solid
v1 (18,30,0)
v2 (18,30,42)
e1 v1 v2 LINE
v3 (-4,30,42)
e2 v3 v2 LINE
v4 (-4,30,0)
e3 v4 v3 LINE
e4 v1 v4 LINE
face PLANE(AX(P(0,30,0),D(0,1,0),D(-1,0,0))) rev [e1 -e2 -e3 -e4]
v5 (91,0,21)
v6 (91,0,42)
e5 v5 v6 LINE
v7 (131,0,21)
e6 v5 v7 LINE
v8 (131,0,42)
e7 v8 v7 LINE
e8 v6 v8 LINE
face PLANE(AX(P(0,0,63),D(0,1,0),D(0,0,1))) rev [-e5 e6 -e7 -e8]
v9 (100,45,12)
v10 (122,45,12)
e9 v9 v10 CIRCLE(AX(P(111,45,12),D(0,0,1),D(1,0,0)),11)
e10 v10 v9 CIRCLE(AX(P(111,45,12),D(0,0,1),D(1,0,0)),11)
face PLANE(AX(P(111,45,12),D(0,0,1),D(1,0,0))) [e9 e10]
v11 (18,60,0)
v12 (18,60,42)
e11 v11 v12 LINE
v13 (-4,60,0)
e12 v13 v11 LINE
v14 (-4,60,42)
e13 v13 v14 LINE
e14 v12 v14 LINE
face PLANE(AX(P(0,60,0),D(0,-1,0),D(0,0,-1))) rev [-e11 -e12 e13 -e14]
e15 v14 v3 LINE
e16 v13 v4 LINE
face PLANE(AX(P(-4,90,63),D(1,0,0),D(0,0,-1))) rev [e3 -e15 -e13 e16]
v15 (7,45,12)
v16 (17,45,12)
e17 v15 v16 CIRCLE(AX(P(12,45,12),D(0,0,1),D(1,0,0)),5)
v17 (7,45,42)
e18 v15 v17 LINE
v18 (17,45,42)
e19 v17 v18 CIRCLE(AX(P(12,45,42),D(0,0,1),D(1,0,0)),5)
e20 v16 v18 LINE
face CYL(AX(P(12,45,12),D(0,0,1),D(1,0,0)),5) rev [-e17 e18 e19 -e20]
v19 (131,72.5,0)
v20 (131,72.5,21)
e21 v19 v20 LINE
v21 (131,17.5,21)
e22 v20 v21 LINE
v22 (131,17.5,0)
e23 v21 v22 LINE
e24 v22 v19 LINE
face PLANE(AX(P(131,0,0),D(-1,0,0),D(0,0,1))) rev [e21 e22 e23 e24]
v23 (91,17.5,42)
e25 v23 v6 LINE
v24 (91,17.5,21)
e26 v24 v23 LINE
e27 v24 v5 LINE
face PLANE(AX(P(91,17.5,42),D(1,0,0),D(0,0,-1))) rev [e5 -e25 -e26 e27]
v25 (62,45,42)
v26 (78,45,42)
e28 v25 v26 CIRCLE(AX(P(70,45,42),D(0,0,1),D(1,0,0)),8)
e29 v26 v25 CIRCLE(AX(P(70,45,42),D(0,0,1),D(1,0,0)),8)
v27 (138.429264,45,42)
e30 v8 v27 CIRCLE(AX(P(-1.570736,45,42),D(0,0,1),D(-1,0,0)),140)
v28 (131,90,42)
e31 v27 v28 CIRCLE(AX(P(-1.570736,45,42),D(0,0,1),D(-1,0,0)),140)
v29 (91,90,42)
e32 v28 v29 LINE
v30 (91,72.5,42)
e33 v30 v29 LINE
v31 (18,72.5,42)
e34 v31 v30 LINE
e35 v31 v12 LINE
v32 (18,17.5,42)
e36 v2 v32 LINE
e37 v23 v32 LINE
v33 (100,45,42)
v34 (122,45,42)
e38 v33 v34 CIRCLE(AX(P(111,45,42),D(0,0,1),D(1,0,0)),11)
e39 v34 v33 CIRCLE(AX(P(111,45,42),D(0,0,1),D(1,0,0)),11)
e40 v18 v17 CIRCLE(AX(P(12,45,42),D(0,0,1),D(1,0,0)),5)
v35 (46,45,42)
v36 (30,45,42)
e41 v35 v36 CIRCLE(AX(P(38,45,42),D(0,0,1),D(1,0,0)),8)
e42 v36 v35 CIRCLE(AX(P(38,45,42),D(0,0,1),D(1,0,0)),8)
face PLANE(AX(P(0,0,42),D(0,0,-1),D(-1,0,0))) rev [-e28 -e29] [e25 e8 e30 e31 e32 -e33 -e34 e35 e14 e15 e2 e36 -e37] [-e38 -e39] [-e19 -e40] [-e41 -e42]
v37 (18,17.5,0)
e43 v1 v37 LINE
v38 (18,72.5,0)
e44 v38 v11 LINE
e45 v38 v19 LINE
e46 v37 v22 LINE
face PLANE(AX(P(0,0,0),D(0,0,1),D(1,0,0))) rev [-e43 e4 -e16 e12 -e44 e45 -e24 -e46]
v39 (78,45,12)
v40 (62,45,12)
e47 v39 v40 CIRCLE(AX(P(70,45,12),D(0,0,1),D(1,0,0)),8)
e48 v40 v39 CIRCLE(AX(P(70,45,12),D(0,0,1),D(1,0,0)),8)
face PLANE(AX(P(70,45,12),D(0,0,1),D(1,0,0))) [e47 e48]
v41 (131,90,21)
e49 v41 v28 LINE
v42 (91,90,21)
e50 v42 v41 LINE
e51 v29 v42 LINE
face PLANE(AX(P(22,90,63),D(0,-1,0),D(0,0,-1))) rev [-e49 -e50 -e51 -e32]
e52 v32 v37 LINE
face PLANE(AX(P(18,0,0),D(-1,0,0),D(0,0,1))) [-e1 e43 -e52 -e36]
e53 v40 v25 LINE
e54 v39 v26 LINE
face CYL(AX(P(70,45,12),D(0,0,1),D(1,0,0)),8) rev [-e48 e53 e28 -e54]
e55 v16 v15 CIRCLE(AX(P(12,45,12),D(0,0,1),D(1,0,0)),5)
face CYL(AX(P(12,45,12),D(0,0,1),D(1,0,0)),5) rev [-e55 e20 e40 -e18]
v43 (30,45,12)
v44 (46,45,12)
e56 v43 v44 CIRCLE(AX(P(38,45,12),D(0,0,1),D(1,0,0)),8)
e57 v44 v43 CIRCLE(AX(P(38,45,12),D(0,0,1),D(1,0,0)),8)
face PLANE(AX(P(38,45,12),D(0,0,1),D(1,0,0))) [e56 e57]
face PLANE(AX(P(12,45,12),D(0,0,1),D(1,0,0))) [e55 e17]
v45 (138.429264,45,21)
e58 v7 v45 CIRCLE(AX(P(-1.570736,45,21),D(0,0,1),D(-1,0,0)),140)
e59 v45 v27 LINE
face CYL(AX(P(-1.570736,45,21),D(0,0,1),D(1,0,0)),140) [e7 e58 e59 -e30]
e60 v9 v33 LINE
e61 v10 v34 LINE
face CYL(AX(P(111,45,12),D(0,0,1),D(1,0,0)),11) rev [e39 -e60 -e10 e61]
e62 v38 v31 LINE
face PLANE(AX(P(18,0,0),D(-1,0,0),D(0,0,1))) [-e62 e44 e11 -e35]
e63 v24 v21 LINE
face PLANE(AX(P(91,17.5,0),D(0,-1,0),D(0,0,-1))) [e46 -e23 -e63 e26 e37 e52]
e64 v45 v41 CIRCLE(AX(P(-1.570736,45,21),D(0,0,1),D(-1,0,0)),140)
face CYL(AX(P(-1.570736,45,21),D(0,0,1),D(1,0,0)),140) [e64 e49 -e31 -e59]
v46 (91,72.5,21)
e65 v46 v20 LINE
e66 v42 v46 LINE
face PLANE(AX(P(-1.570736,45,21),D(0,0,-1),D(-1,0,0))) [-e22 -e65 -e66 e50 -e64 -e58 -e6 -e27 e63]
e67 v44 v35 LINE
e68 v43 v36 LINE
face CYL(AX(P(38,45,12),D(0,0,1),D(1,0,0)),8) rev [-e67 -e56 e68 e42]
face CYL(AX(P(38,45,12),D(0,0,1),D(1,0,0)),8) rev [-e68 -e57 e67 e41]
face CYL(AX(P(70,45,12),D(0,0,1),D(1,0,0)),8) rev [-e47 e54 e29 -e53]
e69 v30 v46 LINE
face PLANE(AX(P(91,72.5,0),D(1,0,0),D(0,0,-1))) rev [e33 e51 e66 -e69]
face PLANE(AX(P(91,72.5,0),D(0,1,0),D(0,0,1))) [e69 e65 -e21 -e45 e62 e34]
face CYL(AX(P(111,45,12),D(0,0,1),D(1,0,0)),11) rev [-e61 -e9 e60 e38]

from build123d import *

# Parameters (mm, degrees)
BASE_BLOCK_63MM_DEPTH      = 63
PROFILE_CUT_63MM_DEPTH     = 63
SIDE_BOSS_SKETCH_W         = 63
SIDE_BOSS_SKETCH_H         = 90
SIDE_BOSS_16MM_DEPTH       = 16
STEP_CUT_21MM_DEPTH        = 21
CURVED_END_BOSS_21MM_DEPTH = 21
POCKET_CUT_SKETCH_W        = 21
POCKET_CUT_SKETCH_H        = 17.5
POCKET_CUT_40MM_DEPTH      = 40
HOLE_A_SKETCH_W            = 73
HOLE_A_SKETCH_H            = 42
HOLE_A_17_5MM_DEEP_DEPTH   = 17.5
HOLE_B_SKETCH_W            = 73
HOLE_B_SKETCH_H            = 42
HOLE_B_17_5MM_DEEP_DEPTH   = 17.5
END_CUT_SKETCH_R           = 11
END_CUT_SKETCH_R_2         = 8
END_CUT_SKETCH_R_3         = 5
END_CUT_30MM_DEPTH         = 30


with BuildPart() as part:
    # Base Profile Sketch → Base Block 63mm (new body)
    with BuildSketch(Plane.XY):
        Polygon((0, 0), (115, 0), (115, 90), (54, 90), (22, 90), (-4, 90), (-4, 0), align=None)
    extrude(amount=BASE_BLOCK_63MM_DEPTH)

    # Profile Cut Sketch → Profile Cut 63mm (cut)
    with BuildSketch(Plane.XY.offset(63)):
        Polygon((18, 60), (18, 72.5), (18, 90), (-4, 90), (-4, 72.5), (-4, 60), align=None)
        Polygon((18, 30), (-4, 30), (-4, 17.5), (-4, 0), (18, 0), (18, 17.5), align=None)
    extrude(amount=-PROFILE_CUT_63MM_DEPTH, mode=Mode.SUBTRACT)

    # Side Boss Sketch → Side Boss 16mm (add)
    with BuildSketch(Plane(origin=(115, 0, 0), x_dir=(0, 0, -1), z_dir=(1, 0, 0))):
        with Locations((-31.5, 45)):
            Rectangle(SIDE_BOSS_SKETCH_W, SIDE_BOSS_SKETCH_H)
    extrude(amount=SIDE_BOSS_16MM_DEPTH)

    # Step Cut Sketch → Step Cut 21mm (cut)
    with BuildSketch(Plane.XY.offset(63)):
        Polygon((18, 90), (91, 90), (131, 90), (131, 0), (91, 0), (18, 0), (18, 30), (-4, 30), (-4, 60), (18, 60), align=None)
    extrude(amount=-STEP_CUT_21MM_DEPTH, mode=Mode.SUBTRACT)

    # Curved End Boss Sketch → Curved End Boss 21mm (add)
    with BuildSketch(Plane.XY.offset(42)):
        with BuildLine():
            Line((131, 90), (131, 0))
            ThreePointArc((131, 0), (138.429264164, 45), (131, 90))
        make_face()
    extrude(amount=-CURVED_END_BOSS_21MM_DEPTH)

    # Pocket Cut Sketch → Pocket Cut 40mm (cut)
    with BuildSketch(Plane(origin=(131, 0, 0), x_dir=(0, 0, -1), z_dir=(1, 0, 0))):
        with Locations((-10.5, 81.25)):
            Rectangle(POCKET_CUT_SKETCH_W, POCKET_CUT_SKETCH_H)
        with Locations((-10.5, 8.75)):
            Rectangle(POCKET_CUT_SKETCH_W, POCKET_CUT_SKETCH_H)
    extrude(amount=-POCKET_CUT_40MM_DEPTH, mode=Mode.SUBTRACT)

    # Hole A Sketch → Hole A 17.5mm Deep (cut)
    with BuildSketch(Plane.XZ):
        with Locations((54.5, 21)):
            Rectangle(HOLE_A_SKETCH_W, HOLE_A_SKETCH_H)
    extrude(amount=-HOLE_A_17_5MM_DEEP_DEPTH, mode=Mode.SUBTRACT)

    # Hole B Sketch → Hole B 17.5mm Deep (cut)
    with BuildSketch(Plane(origin=(0, 90, 0), x_dir=(1, 0, 0), z_dir=(0, 1, 0))):
        with Locations((54.5, -21)):
            Rectangle(HOLE_B_SKETCH_W, HOLE_B_SKETCH_H)
    extrude(amount=-HOLE_B_17_5MM_DEEP_DEPTH, mode=Mode.SUBTRACT)

    # End Cut Sketch → End Cut 30mm (cut)
    with BuildSketch(Plane.XY.offset(42)):
        with Locations((111, 45)):
            Circle(END_CUT_SKETCH_R)
        with Locations((70, 45)):
            Circle(END_CUT_SKETCH_R_2)
        with Locations((38, 45)):
            Circle(END_CUT_SKETCH_R_2)
        with Locations((12, 45)):
            Circle(END_CUT_SKETCH_R_3)
    extrude(amount=-END_CUT_30MM_DEPTH, mode=Mode.SUBTRACT)


solid = part.part
